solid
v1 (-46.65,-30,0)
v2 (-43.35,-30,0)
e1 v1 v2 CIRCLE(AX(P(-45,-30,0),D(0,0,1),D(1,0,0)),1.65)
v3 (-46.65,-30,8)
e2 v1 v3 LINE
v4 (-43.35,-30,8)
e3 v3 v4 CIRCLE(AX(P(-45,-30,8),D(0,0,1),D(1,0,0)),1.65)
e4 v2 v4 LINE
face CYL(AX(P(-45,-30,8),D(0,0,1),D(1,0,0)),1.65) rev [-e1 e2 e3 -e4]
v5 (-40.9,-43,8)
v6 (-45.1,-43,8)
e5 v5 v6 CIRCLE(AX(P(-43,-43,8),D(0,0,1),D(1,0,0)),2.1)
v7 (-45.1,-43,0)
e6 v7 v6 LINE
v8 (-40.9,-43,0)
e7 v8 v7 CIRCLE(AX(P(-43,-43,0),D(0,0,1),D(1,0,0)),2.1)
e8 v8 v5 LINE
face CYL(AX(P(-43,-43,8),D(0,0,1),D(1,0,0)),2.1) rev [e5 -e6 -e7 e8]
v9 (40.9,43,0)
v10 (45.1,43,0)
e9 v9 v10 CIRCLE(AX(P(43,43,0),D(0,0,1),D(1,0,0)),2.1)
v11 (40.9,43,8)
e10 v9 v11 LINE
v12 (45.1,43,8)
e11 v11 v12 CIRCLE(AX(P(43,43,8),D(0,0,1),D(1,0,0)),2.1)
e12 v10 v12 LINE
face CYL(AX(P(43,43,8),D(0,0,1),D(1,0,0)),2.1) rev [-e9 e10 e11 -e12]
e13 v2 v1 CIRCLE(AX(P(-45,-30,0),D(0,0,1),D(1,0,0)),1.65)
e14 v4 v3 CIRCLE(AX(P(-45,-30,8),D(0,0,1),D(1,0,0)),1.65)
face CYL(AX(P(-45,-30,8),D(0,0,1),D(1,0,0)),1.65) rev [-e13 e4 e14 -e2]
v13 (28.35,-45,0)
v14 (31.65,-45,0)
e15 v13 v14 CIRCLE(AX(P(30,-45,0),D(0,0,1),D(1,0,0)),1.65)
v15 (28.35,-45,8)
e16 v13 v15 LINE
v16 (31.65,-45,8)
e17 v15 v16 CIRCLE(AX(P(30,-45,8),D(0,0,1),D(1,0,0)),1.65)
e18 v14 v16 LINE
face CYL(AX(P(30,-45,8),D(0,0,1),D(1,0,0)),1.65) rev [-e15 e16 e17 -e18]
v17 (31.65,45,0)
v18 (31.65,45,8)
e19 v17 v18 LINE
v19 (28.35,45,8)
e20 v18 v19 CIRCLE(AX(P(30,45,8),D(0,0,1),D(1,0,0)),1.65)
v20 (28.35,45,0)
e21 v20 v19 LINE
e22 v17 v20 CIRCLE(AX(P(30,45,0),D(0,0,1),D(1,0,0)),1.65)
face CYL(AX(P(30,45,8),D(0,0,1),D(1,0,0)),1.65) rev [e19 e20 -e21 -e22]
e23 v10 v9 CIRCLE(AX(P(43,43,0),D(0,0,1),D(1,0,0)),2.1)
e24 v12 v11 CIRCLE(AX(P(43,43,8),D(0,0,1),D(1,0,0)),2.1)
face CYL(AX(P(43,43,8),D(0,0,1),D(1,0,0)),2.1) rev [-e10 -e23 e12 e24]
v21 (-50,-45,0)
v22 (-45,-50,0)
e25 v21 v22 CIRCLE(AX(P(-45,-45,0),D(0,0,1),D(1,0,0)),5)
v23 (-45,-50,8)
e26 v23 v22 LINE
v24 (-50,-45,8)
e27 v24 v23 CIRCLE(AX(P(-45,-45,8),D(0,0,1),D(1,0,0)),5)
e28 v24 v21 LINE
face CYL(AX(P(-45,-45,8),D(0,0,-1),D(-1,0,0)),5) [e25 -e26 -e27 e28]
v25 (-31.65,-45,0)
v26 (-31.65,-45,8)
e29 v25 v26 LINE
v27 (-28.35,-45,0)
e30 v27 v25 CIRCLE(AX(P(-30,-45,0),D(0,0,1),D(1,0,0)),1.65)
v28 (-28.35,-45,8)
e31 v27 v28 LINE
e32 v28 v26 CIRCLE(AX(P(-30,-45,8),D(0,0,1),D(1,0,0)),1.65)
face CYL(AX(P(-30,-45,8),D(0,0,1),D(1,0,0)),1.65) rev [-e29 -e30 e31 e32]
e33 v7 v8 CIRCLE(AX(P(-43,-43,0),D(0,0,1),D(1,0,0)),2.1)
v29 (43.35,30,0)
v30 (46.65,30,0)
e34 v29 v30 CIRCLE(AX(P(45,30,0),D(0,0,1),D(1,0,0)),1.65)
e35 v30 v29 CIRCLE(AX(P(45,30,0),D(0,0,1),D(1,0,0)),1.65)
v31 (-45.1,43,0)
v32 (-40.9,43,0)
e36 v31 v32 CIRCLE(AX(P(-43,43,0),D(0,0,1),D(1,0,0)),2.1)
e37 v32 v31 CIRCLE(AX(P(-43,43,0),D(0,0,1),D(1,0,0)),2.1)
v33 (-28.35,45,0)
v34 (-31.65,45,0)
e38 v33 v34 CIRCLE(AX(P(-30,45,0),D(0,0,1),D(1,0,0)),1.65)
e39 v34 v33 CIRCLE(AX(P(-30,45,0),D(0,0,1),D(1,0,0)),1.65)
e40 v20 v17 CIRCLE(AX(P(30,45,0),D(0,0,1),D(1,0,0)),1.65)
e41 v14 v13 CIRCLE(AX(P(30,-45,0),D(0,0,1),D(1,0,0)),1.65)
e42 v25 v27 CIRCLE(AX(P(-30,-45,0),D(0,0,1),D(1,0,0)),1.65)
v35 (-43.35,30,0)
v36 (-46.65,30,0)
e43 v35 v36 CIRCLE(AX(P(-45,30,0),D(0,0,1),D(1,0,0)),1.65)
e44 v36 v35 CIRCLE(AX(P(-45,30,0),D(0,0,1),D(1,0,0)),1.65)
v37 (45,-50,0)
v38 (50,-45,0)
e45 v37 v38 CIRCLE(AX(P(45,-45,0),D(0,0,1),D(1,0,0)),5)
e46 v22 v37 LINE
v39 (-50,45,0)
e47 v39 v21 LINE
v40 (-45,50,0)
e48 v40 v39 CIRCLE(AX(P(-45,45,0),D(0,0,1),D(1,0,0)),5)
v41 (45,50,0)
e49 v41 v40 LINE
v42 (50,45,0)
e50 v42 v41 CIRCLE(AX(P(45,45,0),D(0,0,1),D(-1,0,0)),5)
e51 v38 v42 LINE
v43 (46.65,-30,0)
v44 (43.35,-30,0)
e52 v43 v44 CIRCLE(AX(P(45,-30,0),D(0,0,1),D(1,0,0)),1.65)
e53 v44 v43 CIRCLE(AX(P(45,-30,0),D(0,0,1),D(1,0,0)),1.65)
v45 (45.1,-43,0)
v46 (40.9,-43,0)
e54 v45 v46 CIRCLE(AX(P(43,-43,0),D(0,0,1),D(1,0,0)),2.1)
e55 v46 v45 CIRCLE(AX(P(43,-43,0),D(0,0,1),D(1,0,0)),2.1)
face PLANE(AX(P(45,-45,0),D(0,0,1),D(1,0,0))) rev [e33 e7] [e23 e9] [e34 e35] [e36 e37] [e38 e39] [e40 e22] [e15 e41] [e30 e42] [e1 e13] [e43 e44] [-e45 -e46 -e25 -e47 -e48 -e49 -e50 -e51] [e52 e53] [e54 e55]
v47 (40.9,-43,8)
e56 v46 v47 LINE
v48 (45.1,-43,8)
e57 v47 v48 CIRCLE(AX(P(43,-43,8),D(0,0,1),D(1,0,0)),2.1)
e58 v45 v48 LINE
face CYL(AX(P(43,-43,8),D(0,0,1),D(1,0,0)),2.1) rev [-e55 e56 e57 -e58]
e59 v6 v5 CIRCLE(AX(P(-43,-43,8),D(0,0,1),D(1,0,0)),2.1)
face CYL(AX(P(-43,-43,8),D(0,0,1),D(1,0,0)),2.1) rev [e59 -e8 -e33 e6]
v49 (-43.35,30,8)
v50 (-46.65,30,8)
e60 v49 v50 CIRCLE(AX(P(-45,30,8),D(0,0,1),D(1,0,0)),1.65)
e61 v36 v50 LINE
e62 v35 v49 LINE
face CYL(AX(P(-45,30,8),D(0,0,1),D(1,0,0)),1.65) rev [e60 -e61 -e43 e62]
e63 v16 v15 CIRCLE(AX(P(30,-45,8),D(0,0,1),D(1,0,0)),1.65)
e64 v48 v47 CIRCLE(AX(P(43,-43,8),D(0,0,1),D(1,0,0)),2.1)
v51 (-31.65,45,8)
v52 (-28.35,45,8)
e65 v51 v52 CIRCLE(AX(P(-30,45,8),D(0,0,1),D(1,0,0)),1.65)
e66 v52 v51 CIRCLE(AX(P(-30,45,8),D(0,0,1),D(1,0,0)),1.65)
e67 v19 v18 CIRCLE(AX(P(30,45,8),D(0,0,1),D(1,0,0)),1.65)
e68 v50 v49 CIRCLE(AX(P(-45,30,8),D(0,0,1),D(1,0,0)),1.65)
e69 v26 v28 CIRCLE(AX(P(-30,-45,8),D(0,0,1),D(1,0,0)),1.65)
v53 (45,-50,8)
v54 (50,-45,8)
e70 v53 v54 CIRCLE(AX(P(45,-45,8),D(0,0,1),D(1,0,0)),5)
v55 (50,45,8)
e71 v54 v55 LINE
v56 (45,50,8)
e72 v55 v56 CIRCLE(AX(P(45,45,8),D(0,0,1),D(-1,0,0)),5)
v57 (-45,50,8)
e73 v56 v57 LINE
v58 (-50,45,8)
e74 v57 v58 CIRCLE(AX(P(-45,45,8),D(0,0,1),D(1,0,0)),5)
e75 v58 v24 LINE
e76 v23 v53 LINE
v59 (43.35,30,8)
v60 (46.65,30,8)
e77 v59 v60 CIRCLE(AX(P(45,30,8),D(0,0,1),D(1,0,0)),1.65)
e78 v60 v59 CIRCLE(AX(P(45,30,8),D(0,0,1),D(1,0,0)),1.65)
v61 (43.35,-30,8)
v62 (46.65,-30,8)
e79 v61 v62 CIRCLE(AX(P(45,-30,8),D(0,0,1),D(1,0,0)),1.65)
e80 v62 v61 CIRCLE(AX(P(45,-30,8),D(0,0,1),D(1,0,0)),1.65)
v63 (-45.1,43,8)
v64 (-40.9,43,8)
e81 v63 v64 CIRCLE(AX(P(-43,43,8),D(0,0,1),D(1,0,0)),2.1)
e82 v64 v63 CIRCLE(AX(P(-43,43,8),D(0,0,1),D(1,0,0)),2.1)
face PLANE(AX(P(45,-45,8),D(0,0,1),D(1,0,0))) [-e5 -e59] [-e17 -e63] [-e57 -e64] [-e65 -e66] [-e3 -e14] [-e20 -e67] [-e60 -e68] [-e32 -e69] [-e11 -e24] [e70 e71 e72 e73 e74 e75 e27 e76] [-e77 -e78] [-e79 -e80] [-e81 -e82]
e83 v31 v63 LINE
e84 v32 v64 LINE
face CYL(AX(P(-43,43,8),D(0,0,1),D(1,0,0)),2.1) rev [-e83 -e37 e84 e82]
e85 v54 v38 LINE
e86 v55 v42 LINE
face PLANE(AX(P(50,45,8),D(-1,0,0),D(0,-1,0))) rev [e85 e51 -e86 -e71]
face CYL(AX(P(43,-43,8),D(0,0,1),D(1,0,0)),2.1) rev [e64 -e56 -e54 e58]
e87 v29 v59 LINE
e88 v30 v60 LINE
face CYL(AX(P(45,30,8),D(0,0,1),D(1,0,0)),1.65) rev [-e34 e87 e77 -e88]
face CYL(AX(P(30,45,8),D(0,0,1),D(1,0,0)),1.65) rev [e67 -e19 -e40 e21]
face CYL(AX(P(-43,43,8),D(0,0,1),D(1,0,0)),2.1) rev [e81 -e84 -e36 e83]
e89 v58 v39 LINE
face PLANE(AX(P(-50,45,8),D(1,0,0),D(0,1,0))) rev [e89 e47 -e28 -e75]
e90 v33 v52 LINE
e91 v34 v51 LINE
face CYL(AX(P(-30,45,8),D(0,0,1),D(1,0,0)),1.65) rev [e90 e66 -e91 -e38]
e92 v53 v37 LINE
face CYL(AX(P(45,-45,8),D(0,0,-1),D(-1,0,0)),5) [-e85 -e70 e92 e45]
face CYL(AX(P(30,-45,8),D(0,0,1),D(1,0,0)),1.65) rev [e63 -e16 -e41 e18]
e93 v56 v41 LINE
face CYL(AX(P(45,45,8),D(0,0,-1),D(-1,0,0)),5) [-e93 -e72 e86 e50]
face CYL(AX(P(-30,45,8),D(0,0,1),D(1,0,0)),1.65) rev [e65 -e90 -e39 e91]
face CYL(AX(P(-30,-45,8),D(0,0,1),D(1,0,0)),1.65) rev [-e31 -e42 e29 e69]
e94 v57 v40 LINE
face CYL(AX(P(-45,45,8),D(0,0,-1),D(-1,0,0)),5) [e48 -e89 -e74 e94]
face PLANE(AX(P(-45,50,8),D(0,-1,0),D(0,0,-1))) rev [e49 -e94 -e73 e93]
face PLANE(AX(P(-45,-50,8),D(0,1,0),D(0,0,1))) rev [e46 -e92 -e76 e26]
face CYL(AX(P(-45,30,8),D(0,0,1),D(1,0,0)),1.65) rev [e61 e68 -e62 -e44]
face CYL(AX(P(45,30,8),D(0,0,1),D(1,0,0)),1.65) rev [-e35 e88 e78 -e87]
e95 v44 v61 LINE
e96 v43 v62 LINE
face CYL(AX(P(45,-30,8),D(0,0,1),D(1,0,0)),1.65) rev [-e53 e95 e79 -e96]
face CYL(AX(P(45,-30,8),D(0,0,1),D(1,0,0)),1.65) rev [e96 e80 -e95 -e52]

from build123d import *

# Parameters (mm, degrees)
BOSS_EXTRUDE1_DEPTH   = 8
M5_TAPPED_HOLE1_D     = 4.2
M5_TAPPED_HOLE1_DEPTH = 12.4
M5_TAPPED_HOLE1_TIP   = 1.2618073
M4_TAPPED_HOLE1_D     = 3.3
M4_TAPPED_HOLE1_DEPTH = 10.1
M4_TAPPED_HOLE1_TIP   = 0.991420021


with BuildPart() as part:
    # Sketch1 → Boss-Extrude1 (new body)
    with BuildSketch(Plane.XY):
        with BuildLine():
            Line((-45, 50), (45, 50))
            ThreePointArc((45, 50), (48.535533906, 48.535533906), (50, 45))
            Line((50, 45), (50, -45))
            ThreePointArc((50, -45), (48.535533906, -48.535533906), (45, -50))
            Line((45, -50), (-45, -50))
            ThreePointArc((-45, -50), (-48.535533906, -48.535533906), (-50, -45))
            Line((-50, -45), (-50, 45))
            ThreePointArc((-50, 45), (-48.535533906, 48.535533906), (-45, 50))
        make_face()
    extrude(amount=BOSS_EXTRUDE1_DEPTH)

    # M5 Tapped Hole1
    with Locations(Plane(origin=(-43, 43, 8), x_dir=(1, 0, 0), z_dir=(0, 0, 1))):
        with Locations((0, 0), (86, 0), (86, -86), (0, -86)):
            Hole(M5_TAPPED_HOLE1_D / 2, depth=M5_TAPPED_HOLE1_DEPTH)
            with Locations((0, 0, -(M5_TAPPED_HOLE1_DEPTH + M5_TAPPED_HOLE1_TIP / 2))):  # 118° drill point
                Cone(0, M5_TAPPED_HOLE1_D / 2, M5_TAPPED_HOLE1_TIP, mode=Mode.SUBTRACT)

    # M4 Tapped Hole1
    with Locations(Plane(origin=(-30, -45, 8), x_dir=(1, 0, 0), z_dir=(0, 0, 1))):
        with Locations((0, 0), (60, 0), (-15, 15), (-15, 75), (75, 75), (75, 15), (0, 90), (60, 90)):
            Hole(M4_TAPPED_HOLE1_D / 2, depth=M4_TAPPED_HOLE1_DEPTH)
            with Locations((0, 0, -(M4_TAPPED_HOLE1_DEPTH + M4_TAPPED_HOLE1_TIP / 2))):  # 118° drill point
                Cone(0, M4_TAPPED_HOLE1_D / 2, M4_TAPPED_HOLE1_TIP, mode=Mode.SUBTRACT)


solid = part.part
